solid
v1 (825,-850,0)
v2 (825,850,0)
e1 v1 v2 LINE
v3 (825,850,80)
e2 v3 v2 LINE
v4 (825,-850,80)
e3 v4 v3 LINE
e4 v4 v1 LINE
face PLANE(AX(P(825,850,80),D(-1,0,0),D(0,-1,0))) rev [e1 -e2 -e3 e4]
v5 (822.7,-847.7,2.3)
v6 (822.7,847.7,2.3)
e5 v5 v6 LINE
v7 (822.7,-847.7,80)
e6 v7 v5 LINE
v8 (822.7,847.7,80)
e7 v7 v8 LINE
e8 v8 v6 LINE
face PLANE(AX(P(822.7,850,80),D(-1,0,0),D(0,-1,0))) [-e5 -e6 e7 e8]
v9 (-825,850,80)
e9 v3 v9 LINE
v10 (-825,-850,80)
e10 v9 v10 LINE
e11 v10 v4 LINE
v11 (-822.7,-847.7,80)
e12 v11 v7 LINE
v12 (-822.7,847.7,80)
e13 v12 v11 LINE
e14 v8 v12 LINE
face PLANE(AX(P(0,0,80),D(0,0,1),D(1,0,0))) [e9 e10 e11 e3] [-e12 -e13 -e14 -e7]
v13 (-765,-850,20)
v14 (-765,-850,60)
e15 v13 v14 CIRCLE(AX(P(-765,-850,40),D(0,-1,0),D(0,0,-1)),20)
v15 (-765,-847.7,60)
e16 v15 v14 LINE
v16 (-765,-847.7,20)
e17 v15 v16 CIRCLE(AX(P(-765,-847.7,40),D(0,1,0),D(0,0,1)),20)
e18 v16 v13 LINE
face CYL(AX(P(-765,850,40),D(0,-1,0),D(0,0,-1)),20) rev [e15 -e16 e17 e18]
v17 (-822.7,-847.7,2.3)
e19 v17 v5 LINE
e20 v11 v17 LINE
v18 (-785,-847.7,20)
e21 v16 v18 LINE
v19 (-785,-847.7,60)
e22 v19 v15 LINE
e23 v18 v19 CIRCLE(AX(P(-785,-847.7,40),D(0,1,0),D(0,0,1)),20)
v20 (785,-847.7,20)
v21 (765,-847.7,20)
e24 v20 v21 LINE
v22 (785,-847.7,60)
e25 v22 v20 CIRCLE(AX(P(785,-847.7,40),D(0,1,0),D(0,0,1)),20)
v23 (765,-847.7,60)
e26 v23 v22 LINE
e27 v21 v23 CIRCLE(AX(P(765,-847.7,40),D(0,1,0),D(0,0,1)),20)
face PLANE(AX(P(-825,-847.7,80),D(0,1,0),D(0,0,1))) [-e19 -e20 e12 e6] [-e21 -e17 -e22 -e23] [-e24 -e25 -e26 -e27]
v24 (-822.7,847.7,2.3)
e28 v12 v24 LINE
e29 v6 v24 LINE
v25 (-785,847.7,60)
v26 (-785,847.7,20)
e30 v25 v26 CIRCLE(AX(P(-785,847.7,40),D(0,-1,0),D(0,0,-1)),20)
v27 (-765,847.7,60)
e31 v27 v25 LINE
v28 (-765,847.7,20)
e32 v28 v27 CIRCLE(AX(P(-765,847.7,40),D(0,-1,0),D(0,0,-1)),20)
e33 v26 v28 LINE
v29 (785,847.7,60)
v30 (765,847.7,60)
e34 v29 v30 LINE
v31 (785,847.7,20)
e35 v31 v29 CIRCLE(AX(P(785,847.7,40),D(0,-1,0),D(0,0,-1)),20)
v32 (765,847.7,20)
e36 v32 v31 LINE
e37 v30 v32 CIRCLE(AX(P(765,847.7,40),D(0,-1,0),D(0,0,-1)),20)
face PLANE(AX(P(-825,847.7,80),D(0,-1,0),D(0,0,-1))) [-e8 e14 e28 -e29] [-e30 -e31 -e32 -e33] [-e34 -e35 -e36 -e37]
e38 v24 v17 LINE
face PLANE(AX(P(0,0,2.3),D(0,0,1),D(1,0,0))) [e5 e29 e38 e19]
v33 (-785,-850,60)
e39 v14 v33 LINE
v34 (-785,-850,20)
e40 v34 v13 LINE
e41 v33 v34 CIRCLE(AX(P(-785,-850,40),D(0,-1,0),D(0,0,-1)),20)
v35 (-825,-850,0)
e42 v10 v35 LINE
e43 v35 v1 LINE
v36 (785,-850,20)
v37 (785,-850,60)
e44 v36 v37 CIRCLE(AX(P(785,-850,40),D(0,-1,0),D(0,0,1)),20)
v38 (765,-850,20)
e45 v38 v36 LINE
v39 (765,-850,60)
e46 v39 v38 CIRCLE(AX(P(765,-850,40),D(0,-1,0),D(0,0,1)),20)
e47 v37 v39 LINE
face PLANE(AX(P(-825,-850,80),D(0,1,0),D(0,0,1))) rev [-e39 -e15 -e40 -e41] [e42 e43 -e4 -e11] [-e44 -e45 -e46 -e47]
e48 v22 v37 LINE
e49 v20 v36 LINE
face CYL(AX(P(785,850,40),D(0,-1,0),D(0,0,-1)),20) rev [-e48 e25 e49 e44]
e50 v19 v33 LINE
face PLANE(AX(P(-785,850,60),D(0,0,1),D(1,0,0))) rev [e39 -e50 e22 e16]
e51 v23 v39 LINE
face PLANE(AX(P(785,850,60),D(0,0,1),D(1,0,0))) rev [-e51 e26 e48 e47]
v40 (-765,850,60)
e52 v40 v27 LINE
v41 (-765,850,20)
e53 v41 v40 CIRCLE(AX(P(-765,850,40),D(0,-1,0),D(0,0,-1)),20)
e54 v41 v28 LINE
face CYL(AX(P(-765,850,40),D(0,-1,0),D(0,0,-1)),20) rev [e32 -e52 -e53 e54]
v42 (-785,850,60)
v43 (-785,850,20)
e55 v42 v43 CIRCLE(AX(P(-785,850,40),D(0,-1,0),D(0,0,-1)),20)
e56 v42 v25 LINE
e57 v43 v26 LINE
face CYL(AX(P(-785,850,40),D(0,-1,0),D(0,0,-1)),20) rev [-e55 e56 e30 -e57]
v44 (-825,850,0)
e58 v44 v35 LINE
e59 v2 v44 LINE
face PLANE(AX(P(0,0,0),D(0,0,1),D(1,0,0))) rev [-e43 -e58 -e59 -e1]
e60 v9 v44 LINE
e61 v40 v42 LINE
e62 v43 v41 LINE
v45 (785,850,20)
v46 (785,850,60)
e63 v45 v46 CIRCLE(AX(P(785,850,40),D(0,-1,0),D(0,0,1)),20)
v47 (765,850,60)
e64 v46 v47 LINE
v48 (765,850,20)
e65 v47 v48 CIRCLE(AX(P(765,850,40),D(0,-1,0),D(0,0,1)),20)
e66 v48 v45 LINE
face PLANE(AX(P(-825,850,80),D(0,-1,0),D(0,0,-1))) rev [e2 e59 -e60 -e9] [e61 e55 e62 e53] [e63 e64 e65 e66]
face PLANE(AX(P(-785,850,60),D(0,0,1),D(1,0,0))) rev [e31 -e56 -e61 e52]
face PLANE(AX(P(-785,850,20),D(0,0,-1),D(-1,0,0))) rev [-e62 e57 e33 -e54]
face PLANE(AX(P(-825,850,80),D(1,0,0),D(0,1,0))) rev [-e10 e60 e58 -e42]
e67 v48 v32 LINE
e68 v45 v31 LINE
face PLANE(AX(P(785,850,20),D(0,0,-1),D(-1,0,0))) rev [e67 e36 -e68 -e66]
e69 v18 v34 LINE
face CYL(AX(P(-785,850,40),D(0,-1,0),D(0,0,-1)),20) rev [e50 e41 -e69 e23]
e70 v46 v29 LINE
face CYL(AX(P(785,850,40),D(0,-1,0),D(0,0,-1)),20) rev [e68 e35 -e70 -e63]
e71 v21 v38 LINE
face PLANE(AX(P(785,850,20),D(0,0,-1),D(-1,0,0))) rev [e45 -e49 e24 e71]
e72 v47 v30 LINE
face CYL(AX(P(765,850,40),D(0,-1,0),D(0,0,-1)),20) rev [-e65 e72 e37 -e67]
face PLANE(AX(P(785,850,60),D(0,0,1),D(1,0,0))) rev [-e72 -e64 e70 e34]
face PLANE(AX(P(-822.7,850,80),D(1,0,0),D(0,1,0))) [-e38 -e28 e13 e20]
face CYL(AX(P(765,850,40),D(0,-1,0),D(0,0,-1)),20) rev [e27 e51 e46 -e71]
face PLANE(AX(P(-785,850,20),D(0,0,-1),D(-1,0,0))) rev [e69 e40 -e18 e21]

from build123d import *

# Parameters (mm, degrees)
SKETCH1_W           = 1650
SKETCH1_H           = 1700
BOSS_EXTRUDE1_DEPTH = 80
SHELL1_T            = -2.3
CUT_EXTRUDE1_DEPTH  = 1892.302461268


with BuildPart() as part:
    # Sketch1 → Boss-Extrude1 (new body)
    with BuildSketch(Plane.XY):
        Rectangle(SKETCH1_W, SKETCH1_H)
    extrude(amount=BOSS_EXTRUDE1_DEPTH)

    # Shell1
    shell1_openings = [part.faces().sort_by_distance(p)[0] for p in [
        (0, 0, 80),
    ]]
    offset(amount=SHELL1_T, openings=shell1_openings, kind=Kind.INTERSECTION)

    # Sketch2 → Cut-Extrude1 (cut, through all)
    with BuildSketch(Plane.XZ.offset(850)):
        with BuildLine():
            Line((-785, 60), (-765, 60))
            ThreePointArc((-765, 60), (-745, 40), (-765, 20))
            Line((-765, 20), (-785, 20))
            ThreePointArc((-785, 20), (-805, 40), (-785, 60))
        make_face()
        with BuildLine():
            Line((785, 60), (765, 60))
            ThreePointArc((765, 60), (745, 40), (765, 20))
            Line((765, 20), (785, 20))
            ThreePointArc((785, 20), (805, 40), (785, 60))
        make_face()
    extrude(amount=-CUT_EXTRUDE1_DEPTH, mode=Mode.SUBTRACT)


solid = part.part
